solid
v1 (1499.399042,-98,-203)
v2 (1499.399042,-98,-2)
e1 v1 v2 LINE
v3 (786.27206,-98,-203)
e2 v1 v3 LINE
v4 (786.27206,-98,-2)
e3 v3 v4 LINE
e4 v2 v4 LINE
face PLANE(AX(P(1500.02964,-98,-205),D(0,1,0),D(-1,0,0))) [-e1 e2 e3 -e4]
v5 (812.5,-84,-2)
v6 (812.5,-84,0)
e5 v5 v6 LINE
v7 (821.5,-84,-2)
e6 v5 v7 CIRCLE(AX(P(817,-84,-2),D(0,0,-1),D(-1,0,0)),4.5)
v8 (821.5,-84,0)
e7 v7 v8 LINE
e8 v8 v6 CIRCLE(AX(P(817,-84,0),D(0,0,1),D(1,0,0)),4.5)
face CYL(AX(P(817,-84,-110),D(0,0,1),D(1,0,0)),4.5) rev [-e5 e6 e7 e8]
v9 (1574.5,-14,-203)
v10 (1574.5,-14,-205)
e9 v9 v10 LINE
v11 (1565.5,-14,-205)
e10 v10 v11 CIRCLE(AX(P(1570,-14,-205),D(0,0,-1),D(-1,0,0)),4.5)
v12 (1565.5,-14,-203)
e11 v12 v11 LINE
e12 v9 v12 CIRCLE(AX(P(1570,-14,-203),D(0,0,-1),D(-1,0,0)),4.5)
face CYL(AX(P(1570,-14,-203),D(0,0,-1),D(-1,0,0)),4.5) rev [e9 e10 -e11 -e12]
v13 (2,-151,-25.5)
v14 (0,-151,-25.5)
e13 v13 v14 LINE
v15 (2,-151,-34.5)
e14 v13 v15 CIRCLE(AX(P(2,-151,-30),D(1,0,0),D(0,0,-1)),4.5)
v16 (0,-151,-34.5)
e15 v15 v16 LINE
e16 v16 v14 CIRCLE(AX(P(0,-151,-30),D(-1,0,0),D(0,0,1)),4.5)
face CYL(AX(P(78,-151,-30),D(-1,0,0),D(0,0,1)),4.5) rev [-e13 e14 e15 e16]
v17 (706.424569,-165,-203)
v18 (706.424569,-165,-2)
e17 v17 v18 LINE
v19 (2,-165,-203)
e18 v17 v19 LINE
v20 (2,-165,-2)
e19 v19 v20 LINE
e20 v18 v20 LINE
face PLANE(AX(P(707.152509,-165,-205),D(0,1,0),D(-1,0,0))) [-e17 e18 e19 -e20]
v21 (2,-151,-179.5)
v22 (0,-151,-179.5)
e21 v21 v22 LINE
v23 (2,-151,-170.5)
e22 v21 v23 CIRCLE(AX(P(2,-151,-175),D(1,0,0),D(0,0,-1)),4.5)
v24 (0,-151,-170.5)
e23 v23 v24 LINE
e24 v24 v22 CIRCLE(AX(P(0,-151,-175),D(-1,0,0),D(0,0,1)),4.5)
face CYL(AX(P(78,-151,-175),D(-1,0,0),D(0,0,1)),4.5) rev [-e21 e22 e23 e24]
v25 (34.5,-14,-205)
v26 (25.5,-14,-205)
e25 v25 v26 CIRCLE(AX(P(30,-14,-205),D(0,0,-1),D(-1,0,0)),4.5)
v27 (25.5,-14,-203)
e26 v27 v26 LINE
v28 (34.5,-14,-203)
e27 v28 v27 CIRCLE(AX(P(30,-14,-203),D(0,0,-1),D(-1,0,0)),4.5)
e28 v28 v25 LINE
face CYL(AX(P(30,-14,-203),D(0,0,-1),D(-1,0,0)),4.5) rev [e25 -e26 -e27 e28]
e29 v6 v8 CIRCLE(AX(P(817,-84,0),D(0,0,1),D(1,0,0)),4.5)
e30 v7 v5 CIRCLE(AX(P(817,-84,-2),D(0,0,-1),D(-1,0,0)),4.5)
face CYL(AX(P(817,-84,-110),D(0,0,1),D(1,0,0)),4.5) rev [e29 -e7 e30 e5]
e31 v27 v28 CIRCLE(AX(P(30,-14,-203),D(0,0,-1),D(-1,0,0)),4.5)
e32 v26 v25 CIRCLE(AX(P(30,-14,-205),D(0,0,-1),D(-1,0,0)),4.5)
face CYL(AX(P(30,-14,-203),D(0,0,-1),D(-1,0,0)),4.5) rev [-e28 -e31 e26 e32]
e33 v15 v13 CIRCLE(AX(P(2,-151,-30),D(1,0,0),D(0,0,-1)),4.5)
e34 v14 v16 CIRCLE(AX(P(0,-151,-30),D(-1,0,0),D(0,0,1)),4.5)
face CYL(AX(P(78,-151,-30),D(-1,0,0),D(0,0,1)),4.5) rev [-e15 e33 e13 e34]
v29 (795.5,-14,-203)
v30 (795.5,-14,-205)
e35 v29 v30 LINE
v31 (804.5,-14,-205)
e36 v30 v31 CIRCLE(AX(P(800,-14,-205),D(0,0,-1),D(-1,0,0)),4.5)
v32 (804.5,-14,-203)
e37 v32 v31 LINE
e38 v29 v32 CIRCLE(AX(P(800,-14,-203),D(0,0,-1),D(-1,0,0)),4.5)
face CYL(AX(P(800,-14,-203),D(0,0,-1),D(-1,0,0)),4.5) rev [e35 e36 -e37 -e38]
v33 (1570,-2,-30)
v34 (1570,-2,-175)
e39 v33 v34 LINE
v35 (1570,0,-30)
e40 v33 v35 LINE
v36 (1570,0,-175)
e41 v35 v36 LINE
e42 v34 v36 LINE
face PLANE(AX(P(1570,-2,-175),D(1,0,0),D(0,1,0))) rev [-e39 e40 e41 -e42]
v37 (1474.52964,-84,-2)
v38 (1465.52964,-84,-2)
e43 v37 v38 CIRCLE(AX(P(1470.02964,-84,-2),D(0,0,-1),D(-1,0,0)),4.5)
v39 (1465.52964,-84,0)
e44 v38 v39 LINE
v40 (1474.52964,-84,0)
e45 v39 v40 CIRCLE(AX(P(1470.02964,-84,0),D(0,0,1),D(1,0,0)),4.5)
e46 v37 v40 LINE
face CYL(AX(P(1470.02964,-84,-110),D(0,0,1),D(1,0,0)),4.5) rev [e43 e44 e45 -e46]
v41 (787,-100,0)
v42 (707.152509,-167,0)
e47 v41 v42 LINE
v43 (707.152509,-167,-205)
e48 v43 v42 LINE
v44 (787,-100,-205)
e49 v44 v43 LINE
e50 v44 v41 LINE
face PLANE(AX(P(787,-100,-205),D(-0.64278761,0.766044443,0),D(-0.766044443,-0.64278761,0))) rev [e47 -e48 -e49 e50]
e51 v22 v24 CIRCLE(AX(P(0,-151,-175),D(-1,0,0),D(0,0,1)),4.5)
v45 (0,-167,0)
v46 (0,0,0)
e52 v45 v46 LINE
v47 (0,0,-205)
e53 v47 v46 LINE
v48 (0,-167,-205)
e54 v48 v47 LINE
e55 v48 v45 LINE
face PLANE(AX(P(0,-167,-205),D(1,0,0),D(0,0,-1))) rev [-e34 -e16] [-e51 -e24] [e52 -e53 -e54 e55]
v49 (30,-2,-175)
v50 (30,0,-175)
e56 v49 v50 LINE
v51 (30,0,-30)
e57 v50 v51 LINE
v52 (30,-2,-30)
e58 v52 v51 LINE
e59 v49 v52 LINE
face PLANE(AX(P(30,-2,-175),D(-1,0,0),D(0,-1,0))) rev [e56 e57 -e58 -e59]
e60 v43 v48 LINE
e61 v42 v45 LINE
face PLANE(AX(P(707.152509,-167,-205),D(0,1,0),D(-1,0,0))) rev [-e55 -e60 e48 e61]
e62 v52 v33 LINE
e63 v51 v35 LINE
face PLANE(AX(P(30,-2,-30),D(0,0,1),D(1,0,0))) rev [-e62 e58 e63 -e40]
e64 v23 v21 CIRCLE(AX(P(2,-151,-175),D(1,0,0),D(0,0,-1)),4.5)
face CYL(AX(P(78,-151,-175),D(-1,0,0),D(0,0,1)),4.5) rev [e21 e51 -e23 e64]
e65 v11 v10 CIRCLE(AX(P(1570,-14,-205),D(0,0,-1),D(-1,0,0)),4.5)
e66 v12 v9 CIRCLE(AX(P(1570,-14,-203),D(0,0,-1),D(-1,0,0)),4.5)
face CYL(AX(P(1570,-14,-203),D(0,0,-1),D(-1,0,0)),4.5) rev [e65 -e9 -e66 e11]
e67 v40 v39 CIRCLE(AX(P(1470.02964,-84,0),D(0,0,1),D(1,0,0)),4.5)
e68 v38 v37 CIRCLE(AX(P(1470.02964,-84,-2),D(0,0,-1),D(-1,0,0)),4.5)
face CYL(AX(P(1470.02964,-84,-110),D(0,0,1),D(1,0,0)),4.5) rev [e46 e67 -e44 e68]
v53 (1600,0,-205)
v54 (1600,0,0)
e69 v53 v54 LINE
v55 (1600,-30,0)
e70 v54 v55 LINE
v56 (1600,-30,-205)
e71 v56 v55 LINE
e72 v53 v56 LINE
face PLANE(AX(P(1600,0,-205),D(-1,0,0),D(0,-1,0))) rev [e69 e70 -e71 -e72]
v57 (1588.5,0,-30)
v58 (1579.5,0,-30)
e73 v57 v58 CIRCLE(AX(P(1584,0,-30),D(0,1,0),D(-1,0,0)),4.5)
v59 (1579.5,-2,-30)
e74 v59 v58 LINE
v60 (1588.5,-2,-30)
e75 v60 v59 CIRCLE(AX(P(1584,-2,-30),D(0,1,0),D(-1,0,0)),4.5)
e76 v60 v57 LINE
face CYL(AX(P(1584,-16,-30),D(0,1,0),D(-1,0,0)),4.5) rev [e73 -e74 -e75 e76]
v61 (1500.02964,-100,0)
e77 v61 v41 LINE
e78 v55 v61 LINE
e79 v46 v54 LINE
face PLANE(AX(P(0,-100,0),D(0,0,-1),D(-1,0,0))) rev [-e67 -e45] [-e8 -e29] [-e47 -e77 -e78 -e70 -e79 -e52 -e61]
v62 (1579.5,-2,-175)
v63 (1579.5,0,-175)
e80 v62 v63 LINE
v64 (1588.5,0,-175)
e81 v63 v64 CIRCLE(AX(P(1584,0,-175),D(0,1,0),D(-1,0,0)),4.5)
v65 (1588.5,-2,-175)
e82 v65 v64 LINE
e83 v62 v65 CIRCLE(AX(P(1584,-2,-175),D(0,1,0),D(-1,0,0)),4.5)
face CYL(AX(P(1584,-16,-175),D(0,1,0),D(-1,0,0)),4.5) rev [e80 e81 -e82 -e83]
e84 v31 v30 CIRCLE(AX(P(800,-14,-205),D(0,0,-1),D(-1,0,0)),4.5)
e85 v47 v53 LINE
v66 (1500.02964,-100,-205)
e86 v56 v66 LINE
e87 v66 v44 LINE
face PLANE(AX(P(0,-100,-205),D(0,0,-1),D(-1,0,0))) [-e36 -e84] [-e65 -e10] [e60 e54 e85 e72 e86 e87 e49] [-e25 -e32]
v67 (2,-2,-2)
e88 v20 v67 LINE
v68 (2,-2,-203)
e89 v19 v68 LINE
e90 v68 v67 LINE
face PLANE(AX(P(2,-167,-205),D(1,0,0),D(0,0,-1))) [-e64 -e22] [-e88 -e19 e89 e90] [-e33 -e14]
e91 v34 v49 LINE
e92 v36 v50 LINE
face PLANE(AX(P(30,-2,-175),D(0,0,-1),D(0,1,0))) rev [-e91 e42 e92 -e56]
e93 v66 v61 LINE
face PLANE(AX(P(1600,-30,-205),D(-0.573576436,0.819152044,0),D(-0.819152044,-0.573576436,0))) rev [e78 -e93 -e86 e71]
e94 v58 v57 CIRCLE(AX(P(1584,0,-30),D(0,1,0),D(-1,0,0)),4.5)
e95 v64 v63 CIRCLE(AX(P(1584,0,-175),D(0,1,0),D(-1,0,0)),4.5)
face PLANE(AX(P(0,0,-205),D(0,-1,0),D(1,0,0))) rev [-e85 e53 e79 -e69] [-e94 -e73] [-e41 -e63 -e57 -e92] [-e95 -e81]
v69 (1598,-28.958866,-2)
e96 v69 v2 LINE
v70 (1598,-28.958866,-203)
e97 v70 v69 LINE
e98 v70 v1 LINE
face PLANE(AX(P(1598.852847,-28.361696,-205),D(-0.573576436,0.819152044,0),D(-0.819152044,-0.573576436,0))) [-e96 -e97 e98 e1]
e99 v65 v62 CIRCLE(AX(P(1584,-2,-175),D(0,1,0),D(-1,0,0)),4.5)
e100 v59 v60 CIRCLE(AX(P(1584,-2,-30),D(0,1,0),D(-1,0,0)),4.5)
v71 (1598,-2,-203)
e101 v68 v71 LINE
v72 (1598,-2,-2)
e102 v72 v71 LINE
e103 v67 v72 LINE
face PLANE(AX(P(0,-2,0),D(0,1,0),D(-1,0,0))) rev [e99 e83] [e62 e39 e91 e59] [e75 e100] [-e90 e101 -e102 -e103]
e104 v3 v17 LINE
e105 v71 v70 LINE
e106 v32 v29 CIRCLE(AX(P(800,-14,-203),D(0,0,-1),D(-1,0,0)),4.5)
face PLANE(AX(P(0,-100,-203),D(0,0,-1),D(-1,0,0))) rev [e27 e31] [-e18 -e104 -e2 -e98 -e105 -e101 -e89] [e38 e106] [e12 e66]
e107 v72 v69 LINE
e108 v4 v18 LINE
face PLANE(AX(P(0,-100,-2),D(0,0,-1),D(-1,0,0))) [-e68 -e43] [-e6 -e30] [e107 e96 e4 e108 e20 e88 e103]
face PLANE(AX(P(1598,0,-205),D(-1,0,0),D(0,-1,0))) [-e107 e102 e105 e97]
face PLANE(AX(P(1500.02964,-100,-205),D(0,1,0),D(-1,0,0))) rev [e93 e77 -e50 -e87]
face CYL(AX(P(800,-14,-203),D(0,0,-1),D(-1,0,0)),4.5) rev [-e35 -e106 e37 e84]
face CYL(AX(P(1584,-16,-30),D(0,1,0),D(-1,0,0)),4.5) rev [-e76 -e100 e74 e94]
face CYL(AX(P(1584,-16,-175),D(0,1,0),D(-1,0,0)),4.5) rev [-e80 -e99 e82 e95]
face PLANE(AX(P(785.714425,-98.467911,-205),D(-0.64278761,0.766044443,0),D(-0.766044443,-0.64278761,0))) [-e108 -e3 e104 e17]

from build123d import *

# Parameters (mm, degrees)
EXTRUDE_1_DEPTH     = 205
SHELL_1_T           = -2
SKETCH_4_W          = 1600
SKETCH_4_H          = 205
SKETCH_4_W_2        = 1540
SKETCH_4_H_2        = 145
EXTRUDE_2_DEPTH     = 2
SKETCH_5_R          = 4.5
CUT_EXTRUDE_1_DEPTH = 2
SKETCH_7_R          = 4.5
CUT_EXTRUDE_2_DEPTH = 78
SKETCH_8_R          = 4.5
CUT_EXTRUDE_3_DEPTH = 16
SKETCH_9_R          = 4.5
CUT_EXTRUDE_4_DEPTH = 110


with BuildPart() as part:
    # 草图2 → 凸台-拉伸1 (new body)
    with BuildSketch(Plane(origin=(0, 0, 0), x_dir=(-1, 0, 0), z_dir=(0, 0, -1))):
        Polygon((-1600, -30), (-1500.029639528, -100), (-787, -100), (-707.152509296, -167), (0, -167), (0, 0), (-1600, 0), align=None)
    extrude(amount=EXTRUDE_1_DEPTH)

    # 抽壳1
    shell_1_openings = [part.faces().sort_by_distance(p)[0] for p in [
        (800, 0, -102.5),
    ]]
    offset(amount=SHELL_1_T, openings=shell_1_openings, kind=Kind.INTERSECTION)

    # 草图4 → 凸台-拉伸2 (add)
    with BuildSketch(Plane(origin=(0, 0, 0), x_dir=(1, 0, 0), z_dir=(0, 1, 0))):
        with Locations((800, 102.5)):
            Rectangle(SKETCH_4_W, SKETCH_4_H)
        with Locations((800, 102.5)):
            Rectangle(SKETCH_4_W_2, SKETCH_4_H_2, mode=Mode.SUBTRACT)
    extrude(amount=-EXTRUDE_2_DEPTH)

    # 草图5 → 切除-拉伸1 (cut)
    with BuildSketch(Plane(origin=(0, 0, -205), x_dir=(-1, 0, 0), z_dir=(0, 0, -1))):
        with Locations((-1570, -14)):
            Circle(SKETCH_5_R)
        with Locations((-30, -14)):
            Circle(SKETCH_5_R)
        with Locations((-800, -14)):
            Circle(SKETCH_5_R)
    extrude(amount=-CUT_EXTRUDE_1_DEPTH, mode=Mode.SUBTRACT)

    # 草图7 → 切除-拉伸2 (cut)
    with BuildSketch(Plane.ZY):
        with Locations((-175, -151)):
            Circle(SKETCH_7_R)
        with Locations((-30, -151)):
            Circle(SKETCH_7_R)
    extrude(amount=-CUT_EXTRUDE_2_DEPTH, mode=Mode.SUBTRACT)

    # 草图8 → 切除-拉伸3 (cut)
    with BuildSketch(Plane(origin=(0, 0, 0), x_dir=(1, 0, 0), z_dir=(0, 1, 0))):
        with Locations(Location((1584, 175, 0), (0, 0, 180))):
            Circle(SKETCH_8_R)
        with Locations(Location((1584, 30, 0), (0, 0, 180))):
            Circle(SKETCH_8_R)
    extrude(amount=-CUT_EXTRUDE_3_DEPTH, mode=Mode.SUBTRACT)

    # 草图9 → 切除-拉伸4 (cut)
    with BuildSketch(Plane.XY):
        with Locations((817, -84)):
            Circle(SKETCH_9_R)
        with Locations((1470.029639528, -84)):
            Circle(SKETCH_9_R)
    extrude(amount=-CUT_EXTRUDE_4_DEPTH, mode=Mode.SUBTRACT)


solid = part.part
